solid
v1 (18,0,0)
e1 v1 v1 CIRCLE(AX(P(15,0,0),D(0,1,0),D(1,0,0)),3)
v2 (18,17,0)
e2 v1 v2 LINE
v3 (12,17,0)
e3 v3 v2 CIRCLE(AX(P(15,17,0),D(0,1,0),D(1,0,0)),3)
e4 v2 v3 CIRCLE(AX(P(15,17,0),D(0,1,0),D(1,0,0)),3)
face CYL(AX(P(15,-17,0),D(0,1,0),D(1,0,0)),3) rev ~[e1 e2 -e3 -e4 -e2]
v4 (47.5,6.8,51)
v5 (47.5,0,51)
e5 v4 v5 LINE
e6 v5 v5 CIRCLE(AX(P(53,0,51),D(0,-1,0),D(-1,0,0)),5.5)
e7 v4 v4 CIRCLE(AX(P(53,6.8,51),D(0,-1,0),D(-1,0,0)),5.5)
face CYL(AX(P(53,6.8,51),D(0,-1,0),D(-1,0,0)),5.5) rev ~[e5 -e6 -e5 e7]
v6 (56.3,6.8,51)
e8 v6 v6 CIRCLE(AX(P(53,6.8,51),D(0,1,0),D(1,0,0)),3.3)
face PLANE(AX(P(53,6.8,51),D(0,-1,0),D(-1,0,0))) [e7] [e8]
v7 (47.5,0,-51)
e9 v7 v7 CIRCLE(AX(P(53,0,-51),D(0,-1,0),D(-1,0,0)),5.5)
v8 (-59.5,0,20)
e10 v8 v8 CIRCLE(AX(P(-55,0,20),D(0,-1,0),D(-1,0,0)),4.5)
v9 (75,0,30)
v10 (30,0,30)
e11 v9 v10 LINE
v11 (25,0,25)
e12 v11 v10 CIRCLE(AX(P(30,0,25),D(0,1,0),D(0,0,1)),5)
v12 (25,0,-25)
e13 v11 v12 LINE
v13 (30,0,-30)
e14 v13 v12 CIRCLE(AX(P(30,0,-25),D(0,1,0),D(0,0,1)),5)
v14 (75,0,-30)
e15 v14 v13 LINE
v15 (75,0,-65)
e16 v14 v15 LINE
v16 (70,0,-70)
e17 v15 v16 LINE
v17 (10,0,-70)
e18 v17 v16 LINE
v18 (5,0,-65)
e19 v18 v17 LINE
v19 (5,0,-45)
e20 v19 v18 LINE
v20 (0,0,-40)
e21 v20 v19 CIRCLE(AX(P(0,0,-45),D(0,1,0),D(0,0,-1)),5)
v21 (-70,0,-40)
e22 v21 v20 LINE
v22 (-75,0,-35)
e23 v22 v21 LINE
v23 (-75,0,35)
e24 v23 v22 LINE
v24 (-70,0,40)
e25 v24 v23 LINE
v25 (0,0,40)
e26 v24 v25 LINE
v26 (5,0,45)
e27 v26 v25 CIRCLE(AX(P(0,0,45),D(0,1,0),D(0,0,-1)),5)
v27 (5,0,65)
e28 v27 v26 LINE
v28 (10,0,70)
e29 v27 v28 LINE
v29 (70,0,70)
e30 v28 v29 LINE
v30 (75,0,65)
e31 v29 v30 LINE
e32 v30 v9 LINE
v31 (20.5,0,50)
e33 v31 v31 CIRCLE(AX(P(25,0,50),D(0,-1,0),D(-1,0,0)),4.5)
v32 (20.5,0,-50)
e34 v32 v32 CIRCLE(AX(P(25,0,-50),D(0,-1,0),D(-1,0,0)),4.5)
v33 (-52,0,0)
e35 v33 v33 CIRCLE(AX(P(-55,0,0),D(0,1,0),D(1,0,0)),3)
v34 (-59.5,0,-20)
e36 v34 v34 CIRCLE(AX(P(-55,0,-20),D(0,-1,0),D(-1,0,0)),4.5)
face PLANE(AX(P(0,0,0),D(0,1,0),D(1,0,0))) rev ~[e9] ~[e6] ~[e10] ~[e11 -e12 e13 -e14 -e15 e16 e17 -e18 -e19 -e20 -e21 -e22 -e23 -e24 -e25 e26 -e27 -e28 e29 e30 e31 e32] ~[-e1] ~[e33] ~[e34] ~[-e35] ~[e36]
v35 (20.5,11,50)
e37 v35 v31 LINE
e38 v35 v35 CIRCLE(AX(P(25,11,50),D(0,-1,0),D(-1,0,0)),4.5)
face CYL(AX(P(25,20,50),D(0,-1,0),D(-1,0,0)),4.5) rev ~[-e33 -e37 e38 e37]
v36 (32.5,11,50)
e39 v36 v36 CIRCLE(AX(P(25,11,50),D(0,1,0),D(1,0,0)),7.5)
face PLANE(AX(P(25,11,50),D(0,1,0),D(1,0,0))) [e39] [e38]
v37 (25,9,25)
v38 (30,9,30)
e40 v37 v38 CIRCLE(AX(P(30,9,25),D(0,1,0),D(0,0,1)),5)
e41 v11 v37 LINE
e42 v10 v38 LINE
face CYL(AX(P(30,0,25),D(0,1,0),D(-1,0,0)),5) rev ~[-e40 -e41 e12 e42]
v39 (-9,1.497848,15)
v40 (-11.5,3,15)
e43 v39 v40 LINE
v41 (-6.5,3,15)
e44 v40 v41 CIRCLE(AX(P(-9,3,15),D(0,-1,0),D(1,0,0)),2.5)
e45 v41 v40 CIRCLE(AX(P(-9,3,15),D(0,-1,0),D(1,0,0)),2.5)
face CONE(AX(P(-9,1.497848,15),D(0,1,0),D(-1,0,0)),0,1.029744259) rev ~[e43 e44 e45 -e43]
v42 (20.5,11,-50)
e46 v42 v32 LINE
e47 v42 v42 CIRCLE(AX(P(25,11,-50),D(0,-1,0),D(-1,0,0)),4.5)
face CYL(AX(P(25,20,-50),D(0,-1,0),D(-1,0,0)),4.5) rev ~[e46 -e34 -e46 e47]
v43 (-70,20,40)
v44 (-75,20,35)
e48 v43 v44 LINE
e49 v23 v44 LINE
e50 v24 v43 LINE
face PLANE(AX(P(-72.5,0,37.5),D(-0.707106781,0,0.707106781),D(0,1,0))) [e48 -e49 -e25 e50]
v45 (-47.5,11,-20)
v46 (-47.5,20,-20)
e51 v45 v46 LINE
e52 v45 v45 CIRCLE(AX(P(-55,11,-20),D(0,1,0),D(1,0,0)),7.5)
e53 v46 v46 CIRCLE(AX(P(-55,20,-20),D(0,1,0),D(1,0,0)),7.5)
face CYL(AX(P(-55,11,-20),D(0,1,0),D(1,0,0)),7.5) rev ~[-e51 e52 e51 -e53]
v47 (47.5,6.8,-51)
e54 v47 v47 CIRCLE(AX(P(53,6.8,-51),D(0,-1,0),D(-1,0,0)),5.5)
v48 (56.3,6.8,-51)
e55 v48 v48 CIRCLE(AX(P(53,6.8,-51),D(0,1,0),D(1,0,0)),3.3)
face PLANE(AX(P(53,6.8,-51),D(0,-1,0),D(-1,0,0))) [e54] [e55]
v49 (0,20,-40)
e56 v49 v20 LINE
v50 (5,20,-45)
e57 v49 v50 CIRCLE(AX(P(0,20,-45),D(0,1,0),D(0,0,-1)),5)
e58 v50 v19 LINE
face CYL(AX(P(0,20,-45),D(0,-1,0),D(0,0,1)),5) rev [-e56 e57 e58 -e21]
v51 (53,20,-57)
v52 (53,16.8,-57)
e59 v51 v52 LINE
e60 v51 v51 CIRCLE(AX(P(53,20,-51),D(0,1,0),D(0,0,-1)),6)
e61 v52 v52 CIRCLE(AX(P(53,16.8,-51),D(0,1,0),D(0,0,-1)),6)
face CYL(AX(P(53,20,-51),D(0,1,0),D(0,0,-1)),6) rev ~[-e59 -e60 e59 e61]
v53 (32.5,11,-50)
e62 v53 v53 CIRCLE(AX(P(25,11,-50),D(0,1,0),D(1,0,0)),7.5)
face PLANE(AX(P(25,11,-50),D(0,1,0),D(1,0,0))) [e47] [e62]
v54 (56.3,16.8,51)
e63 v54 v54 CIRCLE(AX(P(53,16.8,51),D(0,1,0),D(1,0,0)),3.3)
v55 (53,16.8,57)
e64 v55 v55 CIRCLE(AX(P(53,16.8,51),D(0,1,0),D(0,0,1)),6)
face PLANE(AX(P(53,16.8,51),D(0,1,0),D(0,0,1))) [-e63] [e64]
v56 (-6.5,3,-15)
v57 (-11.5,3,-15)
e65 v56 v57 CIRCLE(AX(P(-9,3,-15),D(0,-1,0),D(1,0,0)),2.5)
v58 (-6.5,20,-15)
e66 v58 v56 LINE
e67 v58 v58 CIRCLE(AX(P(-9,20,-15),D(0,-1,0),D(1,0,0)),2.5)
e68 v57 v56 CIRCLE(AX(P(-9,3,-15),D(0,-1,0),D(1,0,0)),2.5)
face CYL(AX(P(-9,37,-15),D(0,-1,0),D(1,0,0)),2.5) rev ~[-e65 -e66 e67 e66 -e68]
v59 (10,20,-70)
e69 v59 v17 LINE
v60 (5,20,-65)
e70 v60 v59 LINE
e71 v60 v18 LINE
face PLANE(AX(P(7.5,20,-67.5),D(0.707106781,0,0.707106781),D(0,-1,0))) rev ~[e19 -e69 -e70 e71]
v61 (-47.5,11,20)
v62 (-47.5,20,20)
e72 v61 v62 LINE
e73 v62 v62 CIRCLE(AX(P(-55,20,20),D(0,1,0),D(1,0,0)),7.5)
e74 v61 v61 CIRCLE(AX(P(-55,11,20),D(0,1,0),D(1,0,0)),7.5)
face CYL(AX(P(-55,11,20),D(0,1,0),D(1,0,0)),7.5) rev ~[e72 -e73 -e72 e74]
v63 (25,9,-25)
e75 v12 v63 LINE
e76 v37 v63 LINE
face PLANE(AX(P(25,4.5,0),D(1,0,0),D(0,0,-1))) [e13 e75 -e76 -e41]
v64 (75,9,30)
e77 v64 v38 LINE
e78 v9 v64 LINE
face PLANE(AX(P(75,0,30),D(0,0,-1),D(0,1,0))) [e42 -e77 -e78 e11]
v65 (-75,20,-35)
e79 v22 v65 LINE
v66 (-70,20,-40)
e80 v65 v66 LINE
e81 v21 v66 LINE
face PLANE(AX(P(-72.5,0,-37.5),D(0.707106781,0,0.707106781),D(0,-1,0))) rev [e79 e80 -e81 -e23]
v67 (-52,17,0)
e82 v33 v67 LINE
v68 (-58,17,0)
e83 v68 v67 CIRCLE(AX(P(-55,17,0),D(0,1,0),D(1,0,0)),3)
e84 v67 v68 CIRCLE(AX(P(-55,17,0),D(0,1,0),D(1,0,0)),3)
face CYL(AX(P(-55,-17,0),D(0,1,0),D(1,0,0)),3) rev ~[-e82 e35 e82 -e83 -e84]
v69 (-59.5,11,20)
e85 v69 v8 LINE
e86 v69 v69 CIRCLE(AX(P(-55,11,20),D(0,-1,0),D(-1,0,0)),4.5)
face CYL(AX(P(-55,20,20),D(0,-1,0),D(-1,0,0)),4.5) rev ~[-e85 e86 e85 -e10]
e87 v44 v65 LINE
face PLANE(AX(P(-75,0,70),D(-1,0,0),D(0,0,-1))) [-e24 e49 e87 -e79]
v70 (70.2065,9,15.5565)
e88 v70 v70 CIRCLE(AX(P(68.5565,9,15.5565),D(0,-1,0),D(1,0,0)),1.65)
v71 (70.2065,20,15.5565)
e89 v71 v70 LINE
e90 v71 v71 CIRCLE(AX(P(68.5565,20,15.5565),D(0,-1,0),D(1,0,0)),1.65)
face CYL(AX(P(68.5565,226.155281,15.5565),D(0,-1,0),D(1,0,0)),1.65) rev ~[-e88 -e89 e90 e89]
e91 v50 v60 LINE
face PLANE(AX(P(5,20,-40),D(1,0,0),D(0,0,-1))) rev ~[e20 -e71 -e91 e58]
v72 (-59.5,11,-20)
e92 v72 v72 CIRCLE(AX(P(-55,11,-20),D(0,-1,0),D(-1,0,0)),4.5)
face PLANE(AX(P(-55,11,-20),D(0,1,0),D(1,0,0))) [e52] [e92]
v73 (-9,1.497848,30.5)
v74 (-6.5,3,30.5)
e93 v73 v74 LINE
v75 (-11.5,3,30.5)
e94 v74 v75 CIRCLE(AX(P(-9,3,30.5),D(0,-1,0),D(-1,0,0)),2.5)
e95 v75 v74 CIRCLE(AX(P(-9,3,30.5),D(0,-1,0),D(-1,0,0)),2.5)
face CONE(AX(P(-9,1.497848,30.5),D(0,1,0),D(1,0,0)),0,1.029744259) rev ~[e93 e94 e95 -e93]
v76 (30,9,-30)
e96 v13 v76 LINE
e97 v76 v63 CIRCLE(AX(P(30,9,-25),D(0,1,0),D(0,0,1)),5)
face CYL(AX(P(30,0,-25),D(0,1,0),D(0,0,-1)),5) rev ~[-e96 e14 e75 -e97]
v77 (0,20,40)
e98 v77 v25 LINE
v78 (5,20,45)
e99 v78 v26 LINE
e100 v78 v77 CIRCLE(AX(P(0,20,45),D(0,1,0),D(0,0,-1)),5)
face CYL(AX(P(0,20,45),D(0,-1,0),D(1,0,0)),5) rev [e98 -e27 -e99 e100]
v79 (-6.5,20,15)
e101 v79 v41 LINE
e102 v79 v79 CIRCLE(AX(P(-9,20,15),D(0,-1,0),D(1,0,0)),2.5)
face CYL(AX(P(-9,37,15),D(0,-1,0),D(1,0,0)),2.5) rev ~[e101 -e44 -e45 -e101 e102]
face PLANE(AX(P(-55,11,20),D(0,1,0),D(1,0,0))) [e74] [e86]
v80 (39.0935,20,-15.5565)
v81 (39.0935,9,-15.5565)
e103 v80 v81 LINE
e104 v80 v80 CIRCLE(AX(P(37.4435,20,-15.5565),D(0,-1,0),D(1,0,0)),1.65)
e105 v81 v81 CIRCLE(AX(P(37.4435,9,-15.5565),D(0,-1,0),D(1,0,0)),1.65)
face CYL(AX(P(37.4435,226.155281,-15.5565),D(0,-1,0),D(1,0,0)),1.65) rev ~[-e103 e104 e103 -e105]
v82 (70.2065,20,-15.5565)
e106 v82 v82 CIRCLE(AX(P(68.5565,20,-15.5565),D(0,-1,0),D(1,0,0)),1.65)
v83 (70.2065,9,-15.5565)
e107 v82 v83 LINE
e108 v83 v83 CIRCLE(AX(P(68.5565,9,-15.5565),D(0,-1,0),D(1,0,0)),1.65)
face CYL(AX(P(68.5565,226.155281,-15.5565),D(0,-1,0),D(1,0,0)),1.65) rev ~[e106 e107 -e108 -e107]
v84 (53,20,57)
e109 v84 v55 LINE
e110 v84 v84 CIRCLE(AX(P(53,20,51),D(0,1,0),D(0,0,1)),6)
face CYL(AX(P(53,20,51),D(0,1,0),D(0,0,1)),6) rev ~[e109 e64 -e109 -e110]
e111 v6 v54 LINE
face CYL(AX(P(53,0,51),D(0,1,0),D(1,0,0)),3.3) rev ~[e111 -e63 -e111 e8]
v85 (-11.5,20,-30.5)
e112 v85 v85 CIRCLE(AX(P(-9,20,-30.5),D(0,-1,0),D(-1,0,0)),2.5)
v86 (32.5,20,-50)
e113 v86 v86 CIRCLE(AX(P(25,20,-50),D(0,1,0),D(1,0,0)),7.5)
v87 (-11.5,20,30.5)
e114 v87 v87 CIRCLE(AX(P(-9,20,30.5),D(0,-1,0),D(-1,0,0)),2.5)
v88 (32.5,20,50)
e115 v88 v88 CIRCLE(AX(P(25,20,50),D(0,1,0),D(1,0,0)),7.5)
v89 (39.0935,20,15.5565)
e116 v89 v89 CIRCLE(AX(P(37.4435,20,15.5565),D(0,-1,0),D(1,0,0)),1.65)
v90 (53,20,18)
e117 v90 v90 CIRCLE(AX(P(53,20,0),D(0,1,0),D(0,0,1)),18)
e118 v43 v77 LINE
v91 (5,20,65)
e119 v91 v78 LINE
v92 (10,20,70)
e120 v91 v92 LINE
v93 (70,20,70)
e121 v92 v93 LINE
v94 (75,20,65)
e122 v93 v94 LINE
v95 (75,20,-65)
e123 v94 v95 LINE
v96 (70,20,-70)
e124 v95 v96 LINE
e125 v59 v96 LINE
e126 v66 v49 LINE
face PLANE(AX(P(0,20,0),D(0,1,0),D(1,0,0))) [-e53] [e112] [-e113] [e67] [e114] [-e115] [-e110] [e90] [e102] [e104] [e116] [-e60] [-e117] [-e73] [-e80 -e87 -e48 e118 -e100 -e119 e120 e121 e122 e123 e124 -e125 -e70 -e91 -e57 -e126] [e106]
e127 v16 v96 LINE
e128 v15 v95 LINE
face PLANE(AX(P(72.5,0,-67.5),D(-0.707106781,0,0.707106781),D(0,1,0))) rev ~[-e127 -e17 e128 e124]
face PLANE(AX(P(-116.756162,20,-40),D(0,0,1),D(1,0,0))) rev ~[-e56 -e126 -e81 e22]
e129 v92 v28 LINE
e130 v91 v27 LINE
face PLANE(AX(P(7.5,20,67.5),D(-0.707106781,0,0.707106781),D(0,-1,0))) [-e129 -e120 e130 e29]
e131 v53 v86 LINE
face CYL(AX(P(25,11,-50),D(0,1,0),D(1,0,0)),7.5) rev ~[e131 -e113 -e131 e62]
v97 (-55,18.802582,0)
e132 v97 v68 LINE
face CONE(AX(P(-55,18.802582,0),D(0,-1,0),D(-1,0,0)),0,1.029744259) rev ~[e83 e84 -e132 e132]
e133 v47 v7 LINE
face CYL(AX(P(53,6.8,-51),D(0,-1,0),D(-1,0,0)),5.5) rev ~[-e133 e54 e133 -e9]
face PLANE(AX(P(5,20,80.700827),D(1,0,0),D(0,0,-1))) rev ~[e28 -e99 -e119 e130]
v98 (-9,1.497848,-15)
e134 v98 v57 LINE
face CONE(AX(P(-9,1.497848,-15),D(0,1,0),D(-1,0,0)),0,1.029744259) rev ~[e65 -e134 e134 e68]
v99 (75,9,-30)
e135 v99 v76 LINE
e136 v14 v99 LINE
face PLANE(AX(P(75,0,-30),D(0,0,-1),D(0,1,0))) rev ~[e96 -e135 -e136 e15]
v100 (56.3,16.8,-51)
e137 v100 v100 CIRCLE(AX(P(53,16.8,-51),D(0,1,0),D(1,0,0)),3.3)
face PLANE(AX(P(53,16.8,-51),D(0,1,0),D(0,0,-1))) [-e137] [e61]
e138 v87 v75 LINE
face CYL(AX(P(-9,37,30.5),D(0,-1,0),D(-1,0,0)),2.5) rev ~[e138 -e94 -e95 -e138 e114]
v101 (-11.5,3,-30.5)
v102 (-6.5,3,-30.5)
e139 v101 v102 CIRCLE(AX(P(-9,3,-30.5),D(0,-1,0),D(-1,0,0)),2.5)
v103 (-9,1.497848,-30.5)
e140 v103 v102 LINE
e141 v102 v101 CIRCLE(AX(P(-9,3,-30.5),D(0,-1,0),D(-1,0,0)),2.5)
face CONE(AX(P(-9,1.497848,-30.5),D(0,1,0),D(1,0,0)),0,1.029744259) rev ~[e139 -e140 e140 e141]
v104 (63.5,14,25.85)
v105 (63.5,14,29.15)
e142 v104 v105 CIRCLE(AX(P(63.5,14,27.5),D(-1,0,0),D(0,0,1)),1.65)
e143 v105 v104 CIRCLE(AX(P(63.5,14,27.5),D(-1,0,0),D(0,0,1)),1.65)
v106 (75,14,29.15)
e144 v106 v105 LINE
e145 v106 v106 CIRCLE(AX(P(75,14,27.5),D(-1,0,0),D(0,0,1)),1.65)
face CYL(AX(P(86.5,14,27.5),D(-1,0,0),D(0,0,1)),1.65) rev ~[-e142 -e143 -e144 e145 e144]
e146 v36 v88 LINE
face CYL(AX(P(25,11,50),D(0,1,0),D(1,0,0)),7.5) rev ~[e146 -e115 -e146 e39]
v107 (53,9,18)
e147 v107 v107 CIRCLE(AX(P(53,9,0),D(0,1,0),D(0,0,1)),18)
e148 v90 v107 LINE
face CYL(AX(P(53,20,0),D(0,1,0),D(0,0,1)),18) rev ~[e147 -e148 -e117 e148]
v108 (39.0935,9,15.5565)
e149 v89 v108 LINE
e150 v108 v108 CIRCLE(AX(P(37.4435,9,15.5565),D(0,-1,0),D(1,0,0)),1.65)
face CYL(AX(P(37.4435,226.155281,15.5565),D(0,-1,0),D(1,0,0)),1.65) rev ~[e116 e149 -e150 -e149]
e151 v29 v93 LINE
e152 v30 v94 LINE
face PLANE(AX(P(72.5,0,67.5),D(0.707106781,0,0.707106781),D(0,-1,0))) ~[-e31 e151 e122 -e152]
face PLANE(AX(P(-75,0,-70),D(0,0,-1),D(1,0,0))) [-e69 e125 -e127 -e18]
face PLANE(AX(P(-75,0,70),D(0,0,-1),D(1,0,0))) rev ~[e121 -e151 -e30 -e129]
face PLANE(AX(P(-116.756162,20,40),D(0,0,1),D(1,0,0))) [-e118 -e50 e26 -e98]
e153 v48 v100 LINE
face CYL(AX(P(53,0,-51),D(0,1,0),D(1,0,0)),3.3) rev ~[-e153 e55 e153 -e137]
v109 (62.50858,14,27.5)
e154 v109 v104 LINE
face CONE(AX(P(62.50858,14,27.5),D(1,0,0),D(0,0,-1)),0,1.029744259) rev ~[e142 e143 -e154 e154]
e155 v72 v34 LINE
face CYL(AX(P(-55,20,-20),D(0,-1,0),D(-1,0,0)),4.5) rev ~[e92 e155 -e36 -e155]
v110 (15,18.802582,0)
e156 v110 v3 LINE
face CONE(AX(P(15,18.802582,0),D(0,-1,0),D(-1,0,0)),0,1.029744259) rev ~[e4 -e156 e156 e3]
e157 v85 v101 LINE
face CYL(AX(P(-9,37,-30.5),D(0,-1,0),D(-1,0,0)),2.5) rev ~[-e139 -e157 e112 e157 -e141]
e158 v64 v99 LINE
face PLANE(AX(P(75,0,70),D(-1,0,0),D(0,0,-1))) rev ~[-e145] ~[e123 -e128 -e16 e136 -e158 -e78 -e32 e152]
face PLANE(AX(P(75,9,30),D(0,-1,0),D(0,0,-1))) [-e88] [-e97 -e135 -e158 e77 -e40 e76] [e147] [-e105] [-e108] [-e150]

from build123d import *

# Parameters (mm, degrees)
SKETCH1_W                                            = 150
SKETCH1_H                                            = 140
BOSS_EXTRUDE1_DEPTH                                  = 20
CHAMFER1_SIZE                                        = 5
SKETCH4_R                                            = 6
CUT_EXTRUDE1_DEPTH                                   = 3.2
SKETCH7_R                                            = 18
CUT_EXTRUDE2_DEPTH                                   = 105.522724802
M4_TAPPED_HOLE1_D                                    = 3.3
SKETCH14_W                                           = 60
SKETCH14_H                                           = 9
CUT_EXTRUDE5_DEPTH                                   = 50
M4_TAPPED_HOLE3_D                                    = 3.3
M4_TAPPED_HOLE3_DEPTH                                = 11.5
M4_TAPPED_HOLE3_TIP                                  = 0.991420021
FILLET1_R                                            = 5
HOLE_SIZE_PER_SOCKET_HEAD_CAP_SCREW_TYPE_D           = 6.6
HOLE_SIZE_PER_SOCKET_HEAD_CAP_SCREW_TYPE_CBORE_D     = 11
HOLE_SIZE_PER_SOCKET_HEAD_CAP_SCREW_TYPE_CBORE_DEPTH = 6.8
SKETCH23_W                                           = 121.756161874
SKETCH23_H                                           = 40
SKETCH23_H_2                                         = 40.700827196
CUT_EXTRUDE6_DEPTH                                   = 105.522724802
FILLET2_R                                            = 5
CHAMFER2_SIZE                                        = 5
HOLE_SIZE_PER_SOCKET_HEAD_CAP_SCREW_2_D              = 9
HOLE_SIZE_PER_SOCKET_HEAD_CAP_SCREW_2_CBORE_D        = 15
HOLE_SIZE_PER_SOCKET_HEAD_CAP_SCREW_2_CBORE_DEPTH    = 9
M6_TAPPED_HOLE1_D                                    = 5
M6_TAPPED_HOLE1_DEPTH                                = 17
M6_TAPPED_HOLE1_TIP                                  = 1.502151548
BLIND_DOWEL_HOLE1_SIZE_MM_D                          = 5
BLIND_DOWEL_HOLE1_SIZE_MM_DEPTH                      = 17
BLIND_DOWEL_HOLE1_SIZE_MM_TIP                        = 1.502151548
F_6_0_6_DIAMETER_HOLE1_D                             = 6
F_6_0_6_DIAMETER_HOLE1_DEPTH                         = 17
F_6_0_6_DIAMETER_HOLE1_TIP                           = 1.802581857


with BuildPart() as part:
    # Sketch1 → Boss-Extrude1 (new body)
    with BuildSketch(Plane(origin=(0, 0, 0), x_dir=(1, 0, 0), z_dir=(0, 1, 0))):
        Rectangle(SKETCH1_W, SKETCH1_H)
    extrude(amount=BOSS_EXTRUDE1_DEPTH)

    # Chamfer1
    chamfer1_edges = [part.edges().sort_by_distance(p)[0] for p in [
        (-75, 10, -70),
        (75, 10, -70),
        (75, 10, 70),
        (-75, 10, 70),
    ]]
    chamfer(chamfer1_edges, length=CHAMFER1_SIZE)

    # Sketch4 → Cut-Extrude1 (cut)
    with BuildSketch(Plane(origin=(0, 20, 0), x_dir=(1, 0, 0), z_dir=(0, 1, 0))):
        with Locations(Location((53, -51, 0), (0, 0, 270))):
            Circle(SKETCH4_R)
        with Locations(Location((53, 51, 0), (0, 0, 90))):
            Circle(SKETCH4_R)
    extrude(amount=-CUT_EXTRUDE1_DEPTH, mode=Mode.SUBTRACT)

    # Sketch7 → Cut-Extrude2 (cut, through all)
    with BuildSketch(Plane(origin=(0, 20, 0), x_dir=(1, 0, 0), z_dir=(0, 1, 0))):
        with Locations(Location((53, 0, 0), (0, 0, 270))):
            Circle(SKETCH7_R)
    extrude(amount=-CUT_EXTRUDE2_DEPTH, mode=Mode.SUBTRACT)

    # M4 Tapped Hole1 (through all)
    with Locations(Plane(origin=(0, 20, 0), x_dir=(-1, 0, 0), z_dir=(0, 1, 0))):
        with Locations((-68.5565, 15.5565), (-68.5565, -15.5565), (-37.4435, -15.5565), (-37.4435, 15.5565)):
            Hole(M4_TAPPED_HOLE1_D / 2)

    # Sketch14 → Cut-Extrude5 (cut)
    with BuildSketch(Plane(origin=(75, 0, 0), x_dir=(0, 0, -1), z_dir=(1, 0, 0))):
        with Locations((0, 4.5)):
            Rectangle(SKETCH14_W, SKETCH14_H)
    extrude(amount=-CUT_EXTRUDE5_DEPTH, mode=Mode.SUBTRACT)

    # M4 Tapped Hole3
    with Locations(Plane(origin=(75, 0, 0), x_dir=(0, 0, -1), z_dir=(1, 0, 0))):
        with Locations((-27.5, 14)):
            Hole(M4_TAPPED_HOLE3_D / 2, depth=M4_TAPPED_HOLE3_DEPTH)
            with Locations((0, 0, -(M4_TAPPED_HOLE3_DEPTH + M4_TAPPED_HOLE3_TIP / 2))):  # 118° drill point
                Cone(0, M4_TAPPED_HOLE3_D / 2, M4_TAPPED_HOLE3_TIP, mode=Mode.SUBTRACT)

    # Fillet1
    fillet1_edges = [part.edges().sort_by_distance(p)[0] for p in [
        (25, 4.5, 30),
        (25, 4.5, -30),
    ]]
    fillet(fillet1_edges, radius=FILLET1_R)

    # Hole size per socket head cap screw type (through all)
    with Locations(Plane(origin=(0, 0, 0), x_dir=(-1, 0, 0), z_dir=(0, -1, 0))):
        with Locations((-53, -51), (-53, 51)):
            CounterBoreHole(HOLE_SIZE_PER_SOCKET_HEAD_CAP_SCREW_TYPE_D / 2, HOLE_SIZE_PER_SOCKET_HEAD_CAP_SCREW_TYPE_CBORE_D / 2, HOLE_SIZE_PER_SOCKET_HEAD_CAP_SCREW_TYPE_CBORE_DEPTH)

    # Sketch23 → Cut-Extrude6 (cut, through all)
    with BuildSketch(Plane(origin=(0, 20, 0), x_dir=(1, 0, 0), z_dir=(0, 1, 0))):
        with Locations((-55.878080937, 60)):
            Rectangle(SKETCH23_W, SKETCH23_H)
        with Locations((-55.878080937, -60.350413598)):
            Rectangle(SKETCH23_W, SKETCH23_H_2)
    extrude(amount=-CUT_EXTRUDE6_DEPTH, mode=Mode.SUBTRACT)

    # Fillet2
    fillet2_edges = [part.edges().sort_by_distance(p)[0] for p in [
        (5, 10, -40),
        (5, 10, 40),
    ]]
    fillet(fillet2_edges, radius=FILLET2_R)

    # Chamfer2
    chamfer2_edges = [part.edges().sort_by_distance(p)[0] for p in [
        (5, 10, -70),
        (-75, 10, -40),
        (5, 10, 70),
        (-75, 10, 40),
    ]]
    chamfer(chamfer2_edges, length=CHAMFER2_SIZE)

    # Hole size per socket head cap screw  2 (through all)
    with Locations(Plane(origin=(0, 20, 0), x_dir=(1, 0, 0), z_dir=(0, 1, 0))):
        with Locations((25, 50), (25, -50), (-55, 20), (-55, -20)):
            CounterBoreHole(HOLE_SIZE_PER_SOCKET_HEAD_CAP_SCREW_2_D / 2, HOLE_SIZE_PER_SOCKET_HEAD_CAP_SCREW_2_CBORE_D / 2, HOLE_SIZE_PER_SOCKET_HEAD_CAP_SCREW_2_CBORE_DEPTH)

    # M6 Tapped Hole1
    with Locations(Plane(origin=(0, 20, 0), x_dir=(1, 0, 0), z_dir=(0, 1, 0))):
        with Locations((-9, 30.5), (-9, -30.5)):
            Hole(M6_TAPPED_HOLE1_D / 2, depth=M6_TAPPED_HOLE1_DEPTH)
            with Locations((0, 0, -(M6_TAPPED_HOLE1_DEPTH + M6_TAPPED_HOLE1_TIP / 2))):  # 118° drill point
                Cone(0, M6_TAPPED_HOLE1_D / 2, M6_TAPPED_HOLE1_TIP, mode=Mode.SUBTRACT)

    # Blind dowel hole1, size mm
    with Locations(Plane(origin=(0, 20, 0), x_dir=(-1, 0, 0), z_dir=(0, 1, 0))):
        with Locations((9, -15), (9, 15)):
            Hole(BLIND_DOWEL_HOLE1_SIZE_MM_D / 2, depth=BLIND_DOWEL_HOLE1_SIZE_MM_DEPTH)
            with Locations((0, 0, -(BLIND_DOWEL_HOLE1_SIZE_MM_DEPTH + BLIND_DOWEL_HOLE1_SIZE_MM_TIP / 2))):  # 118° drill point
                Cone(0, BLIND_DOWEL_HOLE1_SIZE_MM_D / 2, BLIND_DOWEL_HOLE1_SIZE_MM_TIP, mode=Mode.SUBTRACT)

    # Ø6.0 (6) Diameter Hole1
    with Locations(Plane(origin=(0, 0, 0), x_dir=(-1, 0, 0), z_dir=(0, -1, 0))):
        with Locations((55, 0), (-15, 0)):
            Hole(F_6_0_6_DIAMETER_HOLE1_D / 2, depth=F_6_0_6_DIAMETER_HOLE1_DEPTH)
            with Locations((0, 0, -(F_6_0_6_DIAMETER_HOLE1_DEPTH + F_6_0_6_DIAMETER_HOLE1_TIP / 2))):  # 118° drill point
                Cone(0, F_6_0_6_DIAMETER_HOLE1_D / 2, F_6_0_6_DIAMETER_HOLE1_TIP, mode=Mode.SUBTRACT)


solid = part.part
